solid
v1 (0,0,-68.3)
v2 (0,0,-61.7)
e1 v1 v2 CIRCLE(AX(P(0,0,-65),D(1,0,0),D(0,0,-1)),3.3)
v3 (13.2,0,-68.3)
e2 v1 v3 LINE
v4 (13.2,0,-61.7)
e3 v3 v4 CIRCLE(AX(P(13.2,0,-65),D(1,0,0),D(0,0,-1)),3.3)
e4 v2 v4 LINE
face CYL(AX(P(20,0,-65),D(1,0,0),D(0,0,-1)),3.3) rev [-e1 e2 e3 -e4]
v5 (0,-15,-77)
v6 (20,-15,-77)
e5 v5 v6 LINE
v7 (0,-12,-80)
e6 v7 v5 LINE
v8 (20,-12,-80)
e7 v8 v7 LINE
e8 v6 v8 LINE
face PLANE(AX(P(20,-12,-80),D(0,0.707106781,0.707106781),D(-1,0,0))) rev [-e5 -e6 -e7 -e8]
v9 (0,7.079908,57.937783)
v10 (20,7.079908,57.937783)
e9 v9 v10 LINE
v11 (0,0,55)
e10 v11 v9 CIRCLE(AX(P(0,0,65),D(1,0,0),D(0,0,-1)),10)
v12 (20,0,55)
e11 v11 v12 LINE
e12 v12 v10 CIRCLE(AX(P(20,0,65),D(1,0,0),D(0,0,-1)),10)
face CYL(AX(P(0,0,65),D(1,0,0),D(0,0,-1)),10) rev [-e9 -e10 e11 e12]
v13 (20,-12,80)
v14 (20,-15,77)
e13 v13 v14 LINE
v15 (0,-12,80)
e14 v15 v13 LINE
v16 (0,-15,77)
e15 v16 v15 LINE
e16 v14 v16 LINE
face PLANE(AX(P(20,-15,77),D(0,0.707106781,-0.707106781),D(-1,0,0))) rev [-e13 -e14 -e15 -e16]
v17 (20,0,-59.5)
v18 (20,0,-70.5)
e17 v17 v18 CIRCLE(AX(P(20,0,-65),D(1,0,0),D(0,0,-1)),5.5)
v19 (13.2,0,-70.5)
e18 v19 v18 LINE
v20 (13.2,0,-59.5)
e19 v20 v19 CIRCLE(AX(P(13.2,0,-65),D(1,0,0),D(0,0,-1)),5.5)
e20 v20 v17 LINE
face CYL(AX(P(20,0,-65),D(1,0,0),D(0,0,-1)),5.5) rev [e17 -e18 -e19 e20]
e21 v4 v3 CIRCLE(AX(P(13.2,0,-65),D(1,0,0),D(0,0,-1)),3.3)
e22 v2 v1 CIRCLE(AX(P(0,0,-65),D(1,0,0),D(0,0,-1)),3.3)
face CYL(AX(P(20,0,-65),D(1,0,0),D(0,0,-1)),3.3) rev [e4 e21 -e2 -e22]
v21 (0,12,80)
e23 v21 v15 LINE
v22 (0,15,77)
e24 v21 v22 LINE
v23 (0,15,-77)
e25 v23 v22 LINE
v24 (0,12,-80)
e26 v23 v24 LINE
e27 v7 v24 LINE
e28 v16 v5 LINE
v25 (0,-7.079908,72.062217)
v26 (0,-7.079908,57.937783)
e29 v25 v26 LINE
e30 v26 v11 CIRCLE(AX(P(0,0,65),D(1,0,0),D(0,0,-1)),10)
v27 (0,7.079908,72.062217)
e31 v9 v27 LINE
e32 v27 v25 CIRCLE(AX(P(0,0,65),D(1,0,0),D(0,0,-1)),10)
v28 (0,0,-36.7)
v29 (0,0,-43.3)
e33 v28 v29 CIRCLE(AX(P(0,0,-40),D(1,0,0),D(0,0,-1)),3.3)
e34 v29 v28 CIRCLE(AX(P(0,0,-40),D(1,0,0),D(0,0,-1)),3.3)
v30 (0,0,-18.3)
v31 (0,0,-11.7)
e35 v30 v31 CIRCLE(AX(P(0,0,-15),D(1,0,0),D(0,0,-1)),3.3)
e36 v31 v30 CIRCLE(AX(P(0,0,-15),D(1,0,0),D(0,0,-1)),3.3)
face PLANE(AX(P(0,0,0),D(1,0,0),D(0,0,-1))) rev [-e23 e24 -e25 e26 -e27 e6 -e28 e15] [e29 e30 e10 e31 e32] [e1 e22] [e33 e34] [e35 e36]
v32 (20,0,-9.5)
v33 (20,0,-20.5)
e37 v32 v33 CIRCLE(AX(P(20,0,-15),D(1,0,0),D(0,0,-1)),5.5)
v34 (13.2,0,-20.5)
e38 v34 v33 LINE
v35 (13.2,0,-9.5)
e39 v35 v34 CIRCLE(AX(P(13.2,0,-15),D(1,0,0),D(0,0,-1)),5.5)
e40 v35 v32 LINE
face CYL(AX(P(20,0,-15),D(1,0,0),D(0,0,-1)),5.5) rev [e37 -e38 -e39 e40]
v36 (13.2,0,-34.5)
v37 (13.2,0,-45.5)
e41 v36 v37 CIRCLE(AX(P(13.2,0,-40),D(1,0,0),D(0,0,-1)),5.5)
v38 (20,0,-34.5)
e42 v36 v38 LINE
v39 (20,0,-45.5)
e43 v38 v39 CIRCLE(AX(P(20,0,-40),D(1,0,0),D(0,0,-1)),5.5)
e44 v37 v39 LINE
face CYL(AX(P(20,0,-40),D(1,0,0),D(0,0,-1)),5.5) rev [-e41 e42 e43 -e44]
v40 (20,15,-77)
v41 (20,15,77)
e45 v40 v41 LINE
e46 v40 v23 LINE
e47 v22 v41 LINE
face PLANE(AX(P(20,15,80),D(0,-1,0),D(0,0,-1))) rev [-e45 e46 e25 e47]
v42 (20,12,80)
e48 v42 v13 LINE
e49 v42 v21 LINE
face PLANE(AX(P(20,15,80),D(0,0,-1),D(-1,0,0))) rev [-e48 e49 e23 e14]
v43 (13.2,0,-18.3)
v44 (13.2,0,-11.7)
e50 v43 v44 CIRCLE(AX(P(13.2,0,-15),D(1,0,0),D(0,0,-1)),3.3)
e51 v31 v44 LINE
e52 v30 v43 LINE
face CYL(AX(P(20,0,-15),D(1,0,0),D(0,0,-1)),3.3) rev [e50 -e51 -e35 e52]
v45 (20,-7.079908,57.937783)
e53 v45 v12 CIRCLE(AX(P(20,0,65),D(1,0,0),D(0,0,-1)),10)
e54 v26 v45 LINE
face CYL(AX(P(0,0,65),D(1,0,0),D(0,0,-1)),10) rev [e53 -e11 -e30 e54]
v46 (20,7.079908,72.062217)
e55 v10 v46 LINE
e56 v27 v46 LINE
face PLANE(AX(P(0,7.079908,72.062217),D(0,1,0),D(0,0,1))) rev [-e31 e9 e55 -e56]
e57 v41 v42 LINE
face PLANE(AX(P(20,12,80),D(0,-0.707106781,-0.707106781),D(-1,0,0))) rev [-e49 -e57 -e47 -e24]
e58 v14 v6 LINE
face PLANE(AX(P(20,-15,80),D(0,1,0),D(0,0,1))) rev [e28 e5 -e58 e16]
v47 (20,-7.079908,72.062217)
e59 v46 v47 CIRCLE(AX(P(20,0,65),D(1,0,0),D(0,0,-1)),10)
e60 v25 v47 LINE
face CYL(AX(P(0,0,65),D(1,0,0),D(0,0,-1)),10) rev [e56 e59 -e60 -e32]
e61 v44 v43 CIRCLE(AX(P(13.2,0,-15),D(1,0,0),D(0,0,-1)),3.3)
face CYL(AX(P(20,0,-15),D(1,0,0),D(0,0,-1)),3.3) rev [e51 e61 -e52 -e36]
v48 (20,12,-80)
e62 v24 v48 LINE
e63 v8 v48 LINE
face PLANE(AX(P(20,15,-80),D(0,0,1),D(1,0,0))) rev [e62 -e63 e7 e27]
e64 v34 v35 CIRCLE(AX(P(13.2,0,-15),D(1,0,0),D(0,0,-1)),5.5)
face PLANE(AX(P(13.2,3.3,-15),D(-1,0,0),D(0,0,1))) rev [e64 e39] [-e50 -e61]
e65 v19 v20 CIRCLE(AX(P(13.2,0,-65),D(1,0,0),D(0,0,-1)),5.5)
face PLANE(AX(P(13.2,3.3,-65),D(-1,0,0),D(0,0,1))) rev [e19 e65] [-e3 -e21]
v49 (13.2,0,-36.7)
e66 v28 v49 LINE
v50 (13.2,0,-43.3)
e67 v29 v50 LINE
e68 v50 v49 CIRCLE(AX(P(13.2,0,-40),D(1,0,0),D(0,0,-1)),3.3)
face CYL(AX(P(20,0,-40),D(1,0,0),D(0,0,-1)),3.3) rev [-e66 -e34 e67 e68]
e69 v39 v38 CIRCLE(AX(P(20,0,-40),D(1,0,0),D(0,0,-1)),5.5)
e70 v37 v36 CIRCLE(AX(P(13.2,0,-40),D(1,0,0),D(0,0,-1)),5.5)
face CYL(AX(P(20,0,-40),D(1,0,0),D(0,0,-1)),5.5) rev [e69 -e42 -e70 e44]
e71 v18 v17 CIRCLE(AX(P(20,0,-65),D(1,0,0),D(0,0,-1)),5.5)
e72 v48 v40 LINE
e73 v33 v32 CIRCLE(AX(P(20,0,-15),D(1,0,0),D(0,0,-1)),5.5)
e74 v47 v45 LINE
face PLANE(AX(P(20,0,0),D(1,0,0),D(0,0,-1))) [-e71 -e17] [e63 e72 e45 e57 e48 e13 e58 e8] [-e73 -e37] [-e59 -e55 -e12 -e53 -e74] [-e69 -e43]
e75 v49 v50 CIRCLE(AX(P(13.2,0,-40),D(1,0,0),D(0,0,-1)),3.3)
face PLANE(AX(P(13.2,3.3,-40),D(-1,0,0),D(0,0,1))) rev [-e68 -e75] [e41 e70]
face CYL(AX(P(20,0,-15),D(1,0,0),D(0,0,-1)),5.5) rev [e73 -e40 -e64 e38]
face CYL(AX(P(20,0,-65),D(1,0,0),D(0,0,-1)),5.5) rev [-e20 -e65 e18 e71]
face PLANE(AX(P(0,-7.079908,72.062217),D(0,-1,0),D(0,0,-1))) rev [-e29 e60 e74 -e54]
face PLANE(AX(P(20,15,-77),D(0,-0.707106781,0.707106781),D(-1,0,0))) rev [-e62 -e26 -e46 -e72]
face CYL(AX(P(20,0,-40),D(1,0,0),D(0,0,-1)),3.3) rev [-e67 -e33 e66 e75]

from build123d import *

# Parameters (mm, degrees)
SKETCH_1_W                = 160
SKETCH_1_H                = 30
EXTRUDE_1_DEPTH           = 20
CUT_EXTRUDE_1_DEPTH       = 84.815273071
HOLE_WIZARD_1_D           = 6.6
HOLE_WIZARD_1_DEPTH       = 38
HOLE_WIZARD_1_CBORE_D     = 11
HOLE_WIZARD_1_CBORE_DEPTH = 6.8
HOLE_WIZARD_1_TIP         = 1.982840043
CHAMFER_1_SIZE            = 3


with BuildPart() as part:
    # 草图1 → 凸台-拉伸1 (new body)
    with BuildSketch(Plane(origin=(0, 0, 0), x_dir=(0, 0, -1), z_dir=(1, 0, 0))):
        Rectangle(SKETCH_1_W, SKETCH_1_H)
    extrude(amount=EXTRUDE_1_DEPTH)

    # 草图2 → 切除-拉伸1 (cut, through all)
    with BuildSketch(Plane(origin=(20, 0, 0), x_dir=(0, 0, -1), z_dir=(1, 0, 0))):
        with BuildLine():
            Line((-72.062216973, 7.079907586), (-57.937783027, 7.079907586))
            ThreePointArc((-57.937783027, 7.079907586), (-55, 0), (-57.937783027, -7.079907586))
            Line((-57.937783027, -7.079907586), (-72.062216973, -7.079907586))
            ThreePointArc((-72.062216973, -7.079907586), (-75, 0), (-72.062216973, 7.079907586))
        make_face()
    extrude(amount=-CUT_EXTRUDE_1_DEPTH, mode=Mode.SUBTRACT)

    # 打孔尺寸(%根据)内六角圆柱头螺钉的类型1
    with Locations(Plane(origin=(20, 0, 0), x_dir=(0, 0, -1), z_dir=(1, 0, 0))):
        with Locations((15, 0), (40, 0), (65, 0)):
            CounterBoreHole(HOLE_WIZARD_1_D / 2, HOLE_WIZARD_1_CBORE_D / 2, HOLE_WIZARD_1_CBORE_DEPTH, depth=HOLE_WIZARD_1_DEPTH)
            with Locations((0, 0, -(HOLE_WIZARD_1_DEPTH + HOLE_WIZARD_1_TIP / 2))):  # 118° drill point
                Cone(0, HOLE_WIZARD_1_D / 2, HOLE_WIZARD_1_TIP, mode=Mode.SUBTRACT)

    # 倒角1
    chamfer_1_edges = [part.edges().sort_by_distance(p)[0] for p in [
        (10, -15, -80),
        (10, -15, 80),
        (10, 15, 80),
        (10, 15, -80),
    ]]
    chamfer(chamfer_1_edges, length=CHAMFER_1_SIZE)


solid = part.part
